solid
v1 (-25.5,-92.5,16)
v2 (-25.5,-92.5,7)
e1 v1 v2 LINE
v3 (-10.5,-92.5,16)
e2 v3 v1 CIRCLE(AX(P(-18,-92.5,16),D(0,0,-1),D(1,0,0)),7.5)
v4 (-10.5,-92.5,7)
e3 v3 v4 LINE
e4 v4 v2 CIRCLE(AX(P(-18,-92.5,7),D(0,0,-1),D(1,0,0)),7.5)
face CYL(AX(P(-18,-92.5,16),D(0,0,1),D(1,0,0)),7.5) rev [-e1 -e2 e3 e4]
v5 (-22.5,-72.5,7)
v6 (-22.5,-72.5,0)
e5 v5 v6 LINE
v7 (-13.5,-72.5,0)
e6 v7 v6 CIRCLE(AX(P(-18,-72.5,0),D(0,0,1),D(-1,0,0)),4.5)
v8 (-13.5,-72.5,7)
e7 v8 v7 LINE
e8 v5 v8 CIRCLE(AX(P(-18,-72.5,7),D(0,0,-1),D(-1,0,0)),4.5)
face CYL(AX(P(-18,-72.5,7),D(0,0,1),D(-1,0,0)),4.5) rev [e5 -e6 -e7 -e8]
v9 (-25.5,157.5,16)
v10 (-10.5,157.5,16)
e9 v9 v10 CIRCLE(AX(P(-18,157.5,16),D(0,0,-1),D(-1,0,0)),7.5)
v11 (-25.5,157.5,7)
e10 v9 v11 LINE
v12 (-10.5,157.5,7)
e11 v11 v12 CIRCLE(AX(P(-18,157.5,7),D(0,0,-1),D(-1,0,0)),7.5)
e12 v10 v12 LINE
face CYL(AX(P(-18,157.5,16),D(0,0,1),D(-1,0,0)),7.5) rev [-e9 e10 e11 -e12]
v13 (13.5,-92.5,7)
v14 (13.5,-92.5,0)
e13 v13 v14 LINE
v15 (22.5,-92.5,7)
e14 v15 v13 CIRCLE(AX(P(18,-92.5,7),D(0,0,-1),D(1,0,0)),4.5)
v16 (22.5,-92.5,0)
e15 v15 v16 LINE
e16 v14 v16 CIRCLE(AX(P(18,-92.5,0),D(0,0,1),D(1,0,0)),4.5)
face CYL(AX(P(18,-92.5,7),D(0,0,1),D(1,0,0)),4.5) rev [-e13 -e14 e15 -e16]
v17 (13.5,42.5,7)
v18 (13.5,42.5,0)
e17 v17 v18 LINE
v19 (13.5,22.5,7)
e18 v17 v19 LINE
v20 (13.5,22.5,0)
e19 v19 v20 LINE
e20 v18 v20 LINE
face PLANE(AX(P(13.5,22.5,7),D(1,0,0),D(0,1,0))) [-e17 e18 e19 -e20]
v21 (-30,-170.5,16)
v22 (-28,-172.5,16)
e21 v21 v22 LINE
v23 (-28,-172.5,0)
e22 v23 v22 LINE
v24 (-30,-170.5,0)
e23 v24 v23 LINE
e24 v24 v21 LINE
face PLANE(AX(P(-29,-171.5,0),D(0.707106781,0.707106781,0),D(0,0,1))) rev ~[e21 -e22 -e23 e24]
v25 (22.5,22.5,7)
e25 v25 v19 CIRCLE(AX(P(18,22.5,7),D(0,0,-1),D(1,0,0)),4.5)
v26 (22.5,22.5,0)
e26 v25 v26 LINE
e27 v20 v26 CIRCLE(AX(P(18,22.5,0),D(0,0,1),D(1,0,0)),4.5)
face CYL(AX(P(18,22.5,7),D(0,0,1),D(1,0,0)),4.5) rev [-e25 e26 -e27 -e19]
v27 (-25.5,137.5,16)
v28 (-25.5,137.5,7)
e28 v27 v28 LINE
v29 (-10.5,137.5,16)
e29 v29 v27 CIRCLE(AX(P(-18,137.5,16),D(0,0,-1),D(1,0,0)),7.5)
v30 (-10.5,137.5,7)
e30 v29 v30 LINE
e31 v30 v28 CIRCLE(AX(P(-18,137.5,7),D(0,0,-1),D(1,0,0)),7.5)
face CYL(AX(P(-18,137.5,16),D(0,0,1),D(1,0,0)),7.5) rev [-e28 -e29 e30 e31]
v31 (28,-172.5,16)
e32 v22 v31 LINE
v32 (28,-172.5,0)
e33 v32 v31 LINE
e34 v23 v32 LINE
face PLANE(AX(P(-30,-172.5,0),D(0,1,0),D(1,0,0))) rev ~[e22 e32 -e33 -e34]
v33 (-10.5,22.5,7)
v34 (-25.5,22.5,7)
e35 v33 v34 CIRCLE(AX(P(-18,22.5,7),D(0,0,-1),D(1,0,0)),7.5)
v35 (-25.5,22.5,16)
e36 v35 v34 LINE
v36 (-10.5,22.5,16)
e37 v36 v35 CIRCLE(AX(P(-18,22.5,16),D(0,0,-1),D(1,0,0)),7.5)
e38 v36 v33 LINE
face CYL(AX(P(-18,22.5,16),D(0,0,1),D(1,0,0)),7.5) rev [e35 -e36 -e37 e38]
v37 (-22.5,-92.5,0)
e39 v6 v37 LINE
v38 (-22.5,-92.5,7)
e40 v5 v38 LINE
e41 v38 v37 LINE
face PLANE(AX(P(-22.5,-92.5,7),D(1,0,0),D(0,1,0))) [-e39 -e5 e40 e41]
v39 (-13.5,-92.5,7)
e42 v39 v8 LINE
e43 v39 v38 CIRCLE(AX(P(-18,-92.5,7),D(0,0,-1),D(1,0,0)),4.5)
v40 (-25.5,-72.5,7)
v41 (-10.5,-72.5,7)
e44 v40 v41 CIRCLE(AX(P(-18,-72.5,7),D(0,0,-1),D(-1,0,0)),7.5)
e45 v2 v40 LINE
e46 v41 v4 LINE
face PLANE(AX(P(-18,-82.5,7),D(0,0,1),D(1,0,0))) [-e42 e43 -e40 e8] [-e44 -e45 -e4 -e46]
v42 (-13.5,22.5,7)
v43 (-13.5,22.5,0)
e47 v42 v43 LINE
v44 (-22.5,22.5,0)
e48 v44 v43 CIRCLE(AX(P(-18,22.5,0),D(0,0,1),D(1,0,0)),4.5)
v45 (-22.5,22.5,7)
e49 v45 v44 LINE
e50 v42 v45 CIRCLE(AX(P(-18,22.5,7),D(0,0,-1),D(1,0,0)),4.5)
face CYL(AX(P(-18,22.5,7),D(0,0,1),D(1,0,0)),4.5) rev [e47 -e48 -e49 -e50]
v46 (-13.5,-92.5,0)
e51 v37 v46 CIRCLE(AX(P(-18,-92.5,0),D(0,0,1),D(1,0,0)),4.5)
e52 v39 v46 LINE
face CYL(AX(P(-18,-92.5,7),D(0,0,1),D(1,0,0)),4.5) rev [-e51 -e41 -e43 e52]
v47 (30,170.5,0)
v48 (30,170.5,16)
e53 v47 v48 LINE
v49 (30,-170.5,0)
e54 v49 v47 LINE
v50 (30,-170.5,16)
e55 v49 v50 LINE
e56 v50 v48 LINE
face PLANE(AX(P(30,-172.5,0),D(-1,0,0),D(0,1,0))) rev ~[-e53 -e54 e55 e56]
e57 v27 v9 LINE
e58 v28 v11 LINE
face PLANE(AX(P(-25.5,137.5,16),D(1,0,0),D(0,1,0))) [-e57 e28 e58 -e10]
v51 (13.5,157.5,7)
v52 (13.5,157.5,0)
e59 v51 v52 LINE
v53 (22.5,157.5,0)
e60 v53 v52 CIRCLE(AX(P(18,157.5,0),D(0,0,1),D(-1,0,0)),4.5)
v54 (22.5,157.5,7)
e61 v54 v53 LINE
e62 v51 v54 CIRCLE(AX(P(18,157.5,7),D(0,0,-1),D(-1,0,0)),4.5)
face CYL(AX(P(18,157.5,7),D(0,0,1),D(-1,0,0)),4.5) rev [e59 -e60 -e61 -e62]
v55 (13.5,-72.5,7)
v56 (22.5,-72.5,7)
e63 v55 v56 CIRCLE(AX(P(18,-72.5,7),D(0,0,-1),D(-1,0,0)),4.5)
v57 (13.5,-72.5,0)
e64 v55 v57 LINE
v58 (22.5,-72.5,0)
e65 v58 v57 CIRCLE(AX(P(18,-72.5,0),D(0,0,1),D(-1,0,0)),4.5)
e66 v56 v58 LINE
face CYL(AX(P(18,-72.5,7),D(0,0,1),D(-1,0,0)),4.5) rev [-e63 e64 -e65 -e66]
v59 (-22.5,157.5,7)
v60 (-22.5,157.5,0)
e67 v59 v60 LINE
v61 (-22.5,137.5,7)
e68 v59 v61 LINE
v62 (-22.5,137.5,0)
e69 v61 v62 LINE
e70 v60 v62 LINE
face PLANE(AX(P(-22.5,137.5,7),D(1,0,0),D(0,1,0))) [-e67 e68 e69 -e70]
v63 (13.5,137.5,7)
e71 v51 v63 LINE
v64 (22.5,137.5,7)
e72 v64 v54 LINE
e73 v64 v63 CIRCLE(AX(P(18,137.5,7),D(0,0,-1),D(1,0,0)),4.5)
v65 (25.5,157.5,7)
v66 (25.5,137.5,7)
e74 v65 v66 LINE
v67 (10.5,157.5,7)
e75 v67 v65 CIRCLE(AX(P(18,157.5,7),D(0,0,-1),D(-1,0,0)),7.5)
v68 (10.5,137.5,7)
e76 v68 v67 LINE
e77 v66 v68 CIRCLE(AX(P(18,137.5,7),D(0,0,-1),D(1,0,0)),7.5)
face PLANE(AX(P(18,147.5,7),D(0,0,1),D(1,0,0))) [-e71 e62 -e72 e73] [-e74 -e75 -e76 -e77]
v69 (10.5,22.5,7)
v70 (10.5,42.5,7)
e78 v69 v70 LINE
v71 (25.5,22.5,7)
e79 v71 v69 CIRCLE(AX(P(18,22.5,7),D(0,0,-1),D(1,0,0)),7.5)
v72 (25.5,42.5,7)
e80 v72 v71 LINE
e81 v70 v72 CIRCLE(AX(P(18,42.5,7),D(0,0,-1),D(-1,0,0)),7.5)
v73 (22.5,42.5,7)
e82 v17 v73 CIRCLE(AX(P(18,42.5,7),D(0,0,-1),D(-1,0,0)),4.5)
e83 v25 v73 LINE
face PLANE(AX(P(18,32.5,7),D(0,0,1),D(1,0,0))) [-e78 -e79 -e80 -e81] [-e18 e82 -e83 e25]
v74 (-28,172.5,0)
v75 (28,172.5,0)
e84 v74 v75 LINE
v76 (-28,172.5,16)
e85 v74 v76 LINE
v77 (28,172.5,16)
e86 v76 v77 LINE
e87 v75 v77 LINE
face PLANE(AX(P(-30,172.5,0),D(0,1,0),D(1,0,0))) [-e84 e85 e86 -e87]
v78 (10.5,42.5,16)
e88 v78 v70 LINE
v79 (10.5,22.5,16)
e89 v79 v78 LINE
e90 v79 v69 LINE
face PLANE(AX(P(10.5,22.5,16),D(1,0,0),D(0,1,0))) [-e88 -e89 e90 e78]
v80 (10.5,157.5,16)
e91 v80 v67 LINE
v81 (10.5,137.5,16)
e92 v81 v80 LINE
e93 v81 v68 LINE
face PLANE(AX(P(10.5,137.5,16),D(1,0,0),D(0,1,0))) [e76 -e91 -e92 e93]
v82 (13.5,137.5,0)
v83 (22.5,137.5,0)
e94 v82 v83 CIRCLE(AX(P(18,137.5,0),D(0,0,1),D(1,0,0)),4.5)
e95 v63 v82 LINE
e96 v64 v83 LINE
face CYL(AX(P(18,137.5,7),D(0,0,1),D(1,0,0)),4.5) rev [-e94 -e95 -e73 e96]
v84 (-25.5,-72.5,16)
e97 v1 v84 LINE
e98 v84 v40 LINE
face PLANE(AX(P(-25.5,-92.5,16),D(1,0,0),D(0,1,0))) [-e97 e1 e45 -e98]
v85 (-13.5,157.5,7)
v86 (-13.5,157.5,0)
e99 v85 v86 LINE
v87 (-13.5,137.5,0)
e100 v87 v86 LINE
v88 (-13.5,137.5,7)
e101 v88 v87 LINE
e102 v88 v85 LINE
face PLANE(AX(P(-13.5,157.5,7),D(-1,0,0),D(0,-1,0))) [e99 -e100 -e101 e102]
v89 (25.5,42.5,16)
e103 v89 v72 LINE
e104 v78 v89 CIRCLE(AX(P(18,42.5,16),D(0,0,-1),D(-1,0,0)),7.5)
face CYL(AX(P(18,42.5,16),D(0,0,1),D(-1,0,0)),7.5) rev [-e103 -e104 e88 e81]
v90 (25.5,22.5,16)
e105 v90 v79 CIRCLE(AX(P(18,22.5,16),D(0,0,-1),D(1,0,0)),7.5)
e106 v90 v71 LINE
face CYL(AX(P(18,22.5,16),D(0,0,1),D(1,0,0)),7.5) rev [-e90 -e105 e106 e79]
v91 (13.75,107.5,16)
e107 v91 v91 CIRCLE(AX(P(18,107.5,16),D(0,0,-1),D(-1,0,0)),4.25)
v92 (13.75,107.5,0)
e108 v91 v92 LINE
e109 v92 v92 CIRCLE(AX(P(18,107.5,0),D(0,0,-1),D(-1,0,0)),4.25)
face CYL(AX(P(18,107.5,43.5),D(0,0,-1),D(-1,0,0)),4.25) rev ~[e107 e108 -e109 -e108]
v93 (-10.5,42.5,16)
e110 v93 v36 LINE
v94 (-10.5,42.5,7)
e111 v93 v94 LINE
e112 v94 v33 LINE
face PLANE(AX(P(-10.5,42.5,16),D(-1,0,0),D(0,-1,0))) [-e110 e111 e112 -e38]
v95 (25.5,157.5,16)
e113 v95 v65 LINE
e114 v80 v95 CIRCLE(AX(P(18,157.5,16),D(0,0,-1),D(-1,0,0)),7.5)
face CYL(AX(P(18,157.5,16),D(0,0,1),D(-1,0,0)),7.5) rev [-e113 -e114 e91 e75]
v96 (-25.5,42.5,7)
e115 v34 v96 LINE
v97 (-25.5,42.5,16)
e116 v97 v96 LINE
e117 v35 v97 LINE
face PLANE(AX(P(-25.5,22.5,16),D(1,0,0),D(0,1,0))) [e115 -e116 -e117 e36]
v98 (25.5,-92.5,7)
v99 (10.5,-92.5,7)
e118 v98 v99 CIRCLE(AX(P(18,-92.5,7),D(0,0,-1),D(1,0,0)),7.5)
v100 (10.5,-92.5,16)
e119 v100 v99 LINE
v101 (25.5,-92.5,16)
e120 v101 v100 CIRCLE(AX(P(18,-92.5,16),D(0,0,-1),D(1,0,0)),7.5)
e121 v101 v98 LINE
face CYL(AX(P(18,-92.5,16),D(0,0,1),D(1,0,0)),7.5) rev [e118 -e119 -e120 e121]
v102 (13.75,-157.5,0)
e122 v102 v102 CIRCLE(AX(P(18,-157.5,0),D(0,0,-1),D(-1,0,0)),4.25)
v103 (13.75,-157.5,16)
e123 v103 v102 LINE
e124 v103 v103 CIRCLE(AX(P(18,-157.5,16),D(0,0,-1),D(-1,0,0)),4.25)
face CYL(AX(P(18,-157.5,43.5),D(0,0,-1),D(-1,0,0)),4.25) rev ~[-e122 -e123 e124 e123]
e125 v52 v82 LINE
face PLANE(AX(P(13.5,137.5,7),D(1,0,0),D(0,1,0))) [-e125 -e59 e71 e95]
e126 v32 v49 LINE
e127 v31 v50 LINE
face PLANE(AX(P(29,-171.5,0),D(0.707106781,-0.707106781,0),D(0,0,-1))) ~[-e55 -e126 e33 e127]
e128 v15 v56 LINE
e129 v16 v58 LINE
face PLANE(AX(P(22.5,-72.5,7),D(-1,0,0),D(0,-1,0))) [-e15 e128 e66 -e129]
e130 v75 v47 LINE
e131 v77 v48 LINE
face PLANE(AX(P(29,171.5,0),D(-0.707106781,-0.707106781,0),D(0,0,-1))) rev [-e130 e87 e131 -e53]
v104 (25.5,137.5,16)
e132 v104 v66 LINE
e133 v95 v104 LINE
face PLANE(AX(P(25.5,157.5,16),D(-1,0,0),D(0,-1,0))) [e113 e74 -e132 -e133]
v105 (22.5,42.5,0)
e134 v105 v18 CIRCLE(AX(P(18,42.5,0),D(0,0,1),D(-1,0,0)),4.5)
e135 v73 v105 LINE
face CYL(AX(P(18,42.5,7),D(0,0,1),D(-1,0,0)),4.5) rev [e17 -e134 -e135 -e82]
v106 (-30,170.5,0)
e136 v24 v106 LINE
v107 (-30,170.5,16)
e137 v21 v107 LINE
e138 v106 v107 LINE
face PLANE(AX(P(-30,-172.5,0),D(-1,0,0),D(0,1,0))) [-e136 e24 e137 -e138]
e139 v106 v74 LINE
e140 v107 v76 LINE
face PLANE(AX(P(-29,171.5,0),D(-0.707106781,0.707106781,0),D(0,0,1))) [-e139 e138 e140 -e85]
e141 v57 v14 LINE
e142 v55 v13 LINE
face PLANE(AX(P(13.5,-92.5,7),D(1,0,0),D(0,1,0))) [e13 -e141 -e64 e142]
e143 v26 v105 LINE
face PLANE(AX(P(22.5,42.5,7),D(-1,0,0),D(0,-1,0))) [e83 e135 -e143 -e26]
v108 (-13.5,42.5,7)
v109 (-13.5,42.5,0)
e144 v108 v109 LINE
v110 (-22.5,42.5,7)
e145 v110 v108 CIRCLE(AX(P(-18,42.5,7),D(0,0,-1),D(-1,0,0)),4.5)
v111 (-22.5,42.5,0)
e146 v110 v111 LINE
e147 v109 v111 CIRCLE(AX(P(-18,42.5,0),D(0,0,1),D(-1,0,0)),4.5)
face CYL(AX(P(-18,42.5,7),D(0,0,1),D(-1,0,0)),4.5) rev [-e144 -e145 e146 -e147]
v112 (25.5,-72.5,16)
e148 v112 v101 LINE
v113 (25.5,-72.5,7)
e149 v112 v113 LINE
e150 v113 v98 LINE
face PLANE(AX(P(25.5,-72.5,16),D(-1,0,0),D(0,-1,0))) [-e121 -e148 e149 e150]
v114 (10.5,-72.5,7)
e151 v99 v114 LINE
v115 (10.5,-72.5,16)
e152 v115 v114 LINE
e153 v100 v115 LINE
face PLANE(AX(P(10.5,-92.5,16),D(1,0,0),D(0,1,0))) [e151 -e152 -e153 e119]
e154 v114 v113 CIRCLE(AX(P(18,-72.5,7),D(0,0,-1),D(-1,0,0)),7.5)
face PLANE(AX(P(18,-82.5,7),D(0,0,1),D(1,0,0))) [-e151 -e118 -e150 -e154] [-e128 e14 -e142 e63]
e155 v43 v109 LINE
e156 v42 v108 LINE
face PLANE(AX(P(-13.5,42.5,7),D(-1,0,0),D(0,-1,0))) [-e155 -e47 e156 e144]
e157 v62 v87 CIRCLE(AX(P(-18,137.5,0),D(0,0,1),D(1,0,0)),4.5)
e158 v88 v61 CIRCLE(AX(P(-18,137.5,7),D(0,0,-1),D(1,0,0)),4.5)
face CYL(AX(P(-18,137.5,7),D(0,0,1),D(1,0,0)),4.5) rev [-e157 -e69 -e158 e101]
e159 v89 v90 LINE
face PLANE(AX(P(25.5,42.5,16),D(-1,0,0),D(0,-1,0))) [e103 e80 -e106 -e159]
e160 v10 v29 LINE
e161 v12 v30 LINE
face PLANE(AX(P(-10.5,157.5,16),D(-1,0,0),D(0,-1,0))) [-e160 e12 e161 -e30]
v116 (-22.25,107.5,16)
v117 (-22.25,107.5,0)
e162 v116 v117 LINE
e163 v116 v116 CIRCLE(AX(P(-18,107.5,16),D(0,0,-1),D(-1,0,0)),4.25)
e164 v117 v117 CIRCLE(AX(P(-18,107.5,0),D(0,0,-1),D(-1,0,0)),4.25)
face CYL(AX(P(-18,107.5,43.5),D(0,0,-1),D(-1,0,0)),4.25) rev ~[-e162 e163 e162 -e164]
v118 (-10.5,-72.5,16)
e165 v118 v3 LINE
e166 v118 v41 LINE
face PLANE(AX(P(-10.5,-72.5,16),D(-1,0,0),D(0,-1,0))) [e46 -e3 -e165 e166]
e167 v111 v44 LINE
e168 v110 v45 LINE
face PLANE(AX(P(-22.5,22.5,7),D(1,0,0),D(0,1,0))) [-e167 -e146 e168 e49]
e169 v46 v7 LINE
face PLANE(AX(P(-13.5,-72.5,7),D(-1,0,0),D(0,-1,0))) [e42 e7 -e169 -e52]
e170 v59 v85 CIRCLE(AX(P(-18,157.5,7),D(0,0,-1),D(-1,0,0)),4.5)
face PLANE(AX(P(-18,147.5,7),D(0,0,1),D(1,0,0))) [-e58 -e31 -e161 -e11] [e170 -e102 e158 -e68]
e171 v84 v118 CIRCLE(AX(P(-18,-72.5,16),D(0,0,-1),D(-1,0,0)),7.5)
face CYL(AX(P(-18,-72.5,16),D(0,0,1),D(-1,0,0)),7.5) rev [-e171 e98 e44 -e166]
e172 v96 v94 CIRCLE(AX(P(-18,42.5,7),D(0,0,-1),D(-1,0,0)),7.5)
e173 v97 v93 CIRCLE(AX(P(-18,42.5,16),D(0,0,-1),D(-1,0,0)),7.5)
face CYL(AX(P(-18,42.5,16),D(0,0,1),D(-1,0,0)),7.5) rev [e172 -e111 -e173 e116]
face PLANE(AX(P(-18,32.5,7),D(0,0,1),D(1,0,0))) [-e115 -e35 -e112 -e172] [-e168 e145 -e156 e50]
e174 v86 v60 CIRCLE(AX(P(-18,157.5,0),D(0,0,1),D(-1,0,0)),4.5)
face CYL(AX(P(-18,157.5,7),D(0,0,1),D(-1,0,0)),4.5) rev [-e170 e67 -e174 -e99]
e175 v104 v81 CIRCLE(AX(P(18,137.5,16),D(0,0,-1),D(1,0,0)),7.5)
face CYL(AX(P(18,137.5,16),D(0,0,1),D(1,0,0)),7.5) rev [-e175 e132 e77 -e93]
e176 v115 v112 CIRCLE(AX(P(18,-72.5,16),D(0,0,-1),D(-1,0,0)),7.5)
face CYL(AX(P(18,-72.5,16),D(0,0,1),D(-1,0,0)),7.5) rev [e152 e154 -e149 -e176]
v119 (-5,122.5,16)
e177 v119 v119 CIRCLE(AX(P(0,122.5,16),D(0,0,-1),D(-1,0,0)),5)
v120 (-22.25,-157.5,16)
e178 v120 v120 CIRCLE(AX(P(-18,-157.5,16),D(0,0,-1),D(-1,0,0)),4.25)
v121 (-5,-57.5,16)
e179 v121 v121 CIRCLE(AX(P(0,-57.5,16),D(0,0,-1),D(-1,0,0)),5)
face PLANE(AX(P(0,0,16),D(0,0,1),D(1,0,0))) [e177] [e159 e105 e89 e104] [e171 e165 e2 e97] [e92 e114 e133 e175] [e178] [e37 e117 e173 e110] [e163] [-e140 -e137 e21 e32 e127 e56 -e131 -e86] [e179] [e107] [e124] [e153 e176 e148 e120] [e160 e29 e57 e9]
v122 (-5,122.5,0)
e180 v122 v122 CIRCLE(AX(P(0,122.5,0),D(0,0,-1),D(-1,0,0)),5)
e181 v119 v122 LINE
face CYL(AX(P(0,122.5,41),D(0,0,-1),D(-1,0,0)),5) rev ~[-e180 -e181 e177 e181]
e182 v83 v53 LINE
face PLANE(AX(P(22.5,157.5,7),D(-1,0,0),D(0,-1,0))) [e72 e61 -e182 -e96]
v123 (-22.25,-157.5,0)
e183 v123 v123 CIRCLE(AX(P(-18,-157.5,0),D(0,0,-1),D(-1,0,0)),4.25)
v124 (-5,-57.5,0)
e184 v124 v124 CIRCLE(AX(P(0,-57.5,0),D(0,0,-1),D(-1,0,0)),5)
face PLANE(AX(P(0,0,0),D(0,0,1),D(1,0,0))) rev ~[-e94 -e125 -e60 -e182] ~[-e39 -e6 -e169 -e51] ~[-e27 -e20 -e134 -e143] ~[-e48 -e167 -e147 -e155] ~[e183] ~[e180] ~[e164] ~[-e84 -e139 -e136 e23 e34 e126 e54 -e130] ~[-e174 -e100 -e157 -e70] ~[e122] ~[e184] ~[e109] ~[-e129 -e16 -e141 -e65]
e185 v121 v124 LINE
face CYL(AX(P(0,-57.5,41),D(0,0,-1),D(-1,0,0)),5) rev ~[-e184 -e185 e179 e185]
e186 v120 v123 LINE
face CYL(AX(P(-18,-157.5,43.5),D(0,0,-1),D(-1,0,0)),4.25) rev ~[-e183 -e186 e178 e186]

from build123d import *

# Parameters (mm, degrees)
SKETCH_1_W                = 60
SKETCH_1_H                = 345
EXTRUDE_1_DEPTH           = 16
HOLE_WIZARD_1_D           = 9
HOLE_WIZARD_1_CBORE_D     = 15
HOLE_WIZARD_1_CBORE_DEPTH = 9
CHAMFER_1_SIZE            = 2
CUT_EXTRUDE_3_DEPTH       = 9
CUT_EXTRUDE_4_DEPTH       = 176.320420944
HOLE_WIZARD_M10_1_D       = 8.5
HOLE_WIZARD_M10_1_DEPTH   = 27.5
HOLE_WIZARD_M10_1_TIP     = 2.553657631
MM_1_D                    = 10
MM_1_DEPTH                = 25
MM_1_TIP                  = 3.004303095


with BuildPart() as part:
    # 草图1 → 凸台-拉伸1 (new body)
    with BuildSketch(Plane.XY):
        Rectangle(SKETCH_1_W, SKETCH_1_H)
    extrude(amount=EXTRUDE_1_DEPTH)

    # 打孔尺寸(%根据)内六角圆柱头螺钉的类型1 (through all)
    with Locations(Plane.XY.offset(16)):
        with Locations((18, 147.5), (-18, -82.5), (-18, 147.5), (18, -82.5), (-18, 32.5), (18, 32.5)):
            CounterBoreHole(HOLE_WIZARD_1_D / 2, HOLE_WIZARD_1_CBORE_D / 2, HOLE_WIZARD_1_CBORE_DEPTH)

    # 倒角1
    chamfer_1_edges = [part.edges().sort_by_distance(p)[0] for p in [
        (30, -172.5, 8),
        (-30, -172.5, 8),
        (-30, 172.5, 8),
        (30, 172.5, 8),
    ]]
    chamfer(chamfer_1_edges, length=CHAMFER_1_SIZE)

    # 草图7 → 切除-拉伸3 (cut)
    with BuildSketch(Plane.XY.offset(16)):
        with BuildLine():
            Line((-10.5, 157.5), (-10.5, 137.5))
            ThreePointArc((-10.5, 137.5), (-18, 130), (-25.5, 137.5))
            Line((-25.5, 137.5), (-25.5, 157.5))
            ThreePointArc((-25.5, 157.5), (-18, 165), (-10.5, 157.5))
        make_face()
        with BuildLine():
            Line((25.5, 157.5), (25.5, 137.5))
            ThreePointArc((25.5, 137.5), (18, 130), (10.5, 137.5))
            Line((10.5, 137.5), (10.5, 157.5))
            ThreePointArc((10.5, 157.5), (18, 165), (25.5, 157.5))
        make_face()
        with BuildLine():
            Line((-25.5, 22.5), (-25.5, 42.5))
            ThreePointArc((-25.5, 42.5), (-18, 50), (-10.5, 42.5))
            Line((-10.5, 42.5), (-10.5, 22.5))
            ThreePointArc((-10.5, 22.5), (-18, 15), (-25.5, 22.5))
        make_face()
        with BuildLine():
            Line((10.5, 22.5), (10.5, 42.5))
            ThreePointArc((10.5, 42.5), (18, 50), (25.5, 42.5))
            Line((25.5, 42.5), (25.5, 22.5))
            ThreePointArc((25.5, 22.5), (18, 15), (10.5, 22.5))
        make_face()
        with BuildLine():
            Line((-25.5, -92.5), (-25.5, -72.5))
            ThreePointArc((-25.5, -72.5), (-18, -65), (-10.5, -72.5))
            Line((-10.5, -72.5), (-10.5, -92.5))
            ThreePointArc((-10.5, -92.5), (-18, -100), (-25.5, -92.5))
        make_face()
        with BuildLine():
            Line((10.5, -92.5), (10.5, -72.5))
            ThreePointArc((10.5, -72.5), (18, -65), (25.5, -72.5))
            Line((25.5, -72.5), (25.5, -92.5))
            ThreePointArc((25.5, -92.5), (18, -100), (10.5, -92.5))
        make_face()
    extrude(amount=-CUT_EXTRUDE_3_DEPTH, mode=Mode.SUBTRACT)

    # 草图8 → 切除-拉伸4 (cut, through all)
    with BuildSketch(Plane.XY.offset(7)):
        with BuildLine():
            Line((-22.5, 137.5), (-22.5, 157.5))
            ThreePointArc((-22.5, 157.5), (-18, 162), (-13.5, 157.5))
            Line((-13.5, 157.5), (-13.5, 137.5))
            ThreePointArc((-13.5, 137.5), (-18, 133), (-22.5, 137.5))
        make_face()
        with BuildLine():
            Line((13.5, 137.5), (13.5, 157.5))
            ThreePointArc((13.5, 157.5), (18, 162), (22.5, 157.5))
            Line((22.5, 157.5), (22.5, 137.5))
            ThreePointArc((22.5, 137.5), (18, 133), (13.5, 137.5))
        make_face()
        with BuildLine():
            Line((-22.5, 22.5), (-22.5, 42.5))
            ThreePointArc((-22.5, 42.5), (-18, 47), (-13.5, 42.5))
            Line((-13.5, 42.5), (-13.5, 22.5))
            ThreePointArc((-13.5, 22.5), (-18, 18), (-22.5, 22.5))
        make_face()
        with BuildLine():
            Line((13.5, 22.5), (13.5, 42.5))
            ThreePointArc((13.5, 42.5), (18, 47), (22.5, 42.5))
            Line((22.5, 42.5), (22.5, 22.5))
            ThreePointArc((22.5, 22.5), (18, 18), (13.5, 22.5))
        make_face()
        with BuildLine():
            Line((-22.5, -92.5), (-22.5, -72.5))
            ThreePointArc((-22.5, -72.5), (-18, -68), (-13.5, -72.5))
            Line((-13.5, -72.5), (-13.5, -92.5))
            ThreePointArc((-13.5, -92.5), (-18, -97), (-22.5, -92.5))
        make_face()
        with BuildLine():
            Line((13.5, -92.5), (13.5, -72.5))
            ThreePointArc((13.5, -72.5), (18, -68), (22.5, -72.5))
            Line((22.5, -72.5), (22.5, -92.5))
            ThreePointArc((22.5, -92.5), (18, -97), (13.5, -92.5))
        make_face()
    extrude(amount=-CUT_EXTRUDE_4_DEPTH, mode=Mode.SUBTRACT)

    # M10 螺纹孔1
    with Locations(Plane.XY.offset(16)):
        with Locations((-18, 107.5), (18, 107.5), (-18, -157.5), (18, -157.5)):
            Hole(HOLE_WIZARD_M10_1_D / 2, depth=HOLE_WIZARD_M10_1_DEPTH)
            with Locations((0, 0, -(HOLE_WIZARD_M10_1_DEPTH + HOLE_WIZARD_M10_1_TIP / 2))):  # 118° drill point
                Cone(0, HOLE_WIZARD_M10_1_D / 2, HOLE_WIZARD_M10_1_TIP, mode=Mode.SUBTRACT)

    # 大小mm 暗销孔1
    with Locations(Plane.XY.offset(16)):
        with Locations((0, -57.5), (0, 122.5)):
            Hole(MM_1_D / 2, depth=MM_1_DEPTH)
            with Locations((0, 0, -(MM_1_DEPTH + MM_1_TIP / 2))):  # 118° drill point
                Cone(0, MM_1_D / 2, MM_1_TIP, mode=Mode.SUBTRACT)


solid = part.part
